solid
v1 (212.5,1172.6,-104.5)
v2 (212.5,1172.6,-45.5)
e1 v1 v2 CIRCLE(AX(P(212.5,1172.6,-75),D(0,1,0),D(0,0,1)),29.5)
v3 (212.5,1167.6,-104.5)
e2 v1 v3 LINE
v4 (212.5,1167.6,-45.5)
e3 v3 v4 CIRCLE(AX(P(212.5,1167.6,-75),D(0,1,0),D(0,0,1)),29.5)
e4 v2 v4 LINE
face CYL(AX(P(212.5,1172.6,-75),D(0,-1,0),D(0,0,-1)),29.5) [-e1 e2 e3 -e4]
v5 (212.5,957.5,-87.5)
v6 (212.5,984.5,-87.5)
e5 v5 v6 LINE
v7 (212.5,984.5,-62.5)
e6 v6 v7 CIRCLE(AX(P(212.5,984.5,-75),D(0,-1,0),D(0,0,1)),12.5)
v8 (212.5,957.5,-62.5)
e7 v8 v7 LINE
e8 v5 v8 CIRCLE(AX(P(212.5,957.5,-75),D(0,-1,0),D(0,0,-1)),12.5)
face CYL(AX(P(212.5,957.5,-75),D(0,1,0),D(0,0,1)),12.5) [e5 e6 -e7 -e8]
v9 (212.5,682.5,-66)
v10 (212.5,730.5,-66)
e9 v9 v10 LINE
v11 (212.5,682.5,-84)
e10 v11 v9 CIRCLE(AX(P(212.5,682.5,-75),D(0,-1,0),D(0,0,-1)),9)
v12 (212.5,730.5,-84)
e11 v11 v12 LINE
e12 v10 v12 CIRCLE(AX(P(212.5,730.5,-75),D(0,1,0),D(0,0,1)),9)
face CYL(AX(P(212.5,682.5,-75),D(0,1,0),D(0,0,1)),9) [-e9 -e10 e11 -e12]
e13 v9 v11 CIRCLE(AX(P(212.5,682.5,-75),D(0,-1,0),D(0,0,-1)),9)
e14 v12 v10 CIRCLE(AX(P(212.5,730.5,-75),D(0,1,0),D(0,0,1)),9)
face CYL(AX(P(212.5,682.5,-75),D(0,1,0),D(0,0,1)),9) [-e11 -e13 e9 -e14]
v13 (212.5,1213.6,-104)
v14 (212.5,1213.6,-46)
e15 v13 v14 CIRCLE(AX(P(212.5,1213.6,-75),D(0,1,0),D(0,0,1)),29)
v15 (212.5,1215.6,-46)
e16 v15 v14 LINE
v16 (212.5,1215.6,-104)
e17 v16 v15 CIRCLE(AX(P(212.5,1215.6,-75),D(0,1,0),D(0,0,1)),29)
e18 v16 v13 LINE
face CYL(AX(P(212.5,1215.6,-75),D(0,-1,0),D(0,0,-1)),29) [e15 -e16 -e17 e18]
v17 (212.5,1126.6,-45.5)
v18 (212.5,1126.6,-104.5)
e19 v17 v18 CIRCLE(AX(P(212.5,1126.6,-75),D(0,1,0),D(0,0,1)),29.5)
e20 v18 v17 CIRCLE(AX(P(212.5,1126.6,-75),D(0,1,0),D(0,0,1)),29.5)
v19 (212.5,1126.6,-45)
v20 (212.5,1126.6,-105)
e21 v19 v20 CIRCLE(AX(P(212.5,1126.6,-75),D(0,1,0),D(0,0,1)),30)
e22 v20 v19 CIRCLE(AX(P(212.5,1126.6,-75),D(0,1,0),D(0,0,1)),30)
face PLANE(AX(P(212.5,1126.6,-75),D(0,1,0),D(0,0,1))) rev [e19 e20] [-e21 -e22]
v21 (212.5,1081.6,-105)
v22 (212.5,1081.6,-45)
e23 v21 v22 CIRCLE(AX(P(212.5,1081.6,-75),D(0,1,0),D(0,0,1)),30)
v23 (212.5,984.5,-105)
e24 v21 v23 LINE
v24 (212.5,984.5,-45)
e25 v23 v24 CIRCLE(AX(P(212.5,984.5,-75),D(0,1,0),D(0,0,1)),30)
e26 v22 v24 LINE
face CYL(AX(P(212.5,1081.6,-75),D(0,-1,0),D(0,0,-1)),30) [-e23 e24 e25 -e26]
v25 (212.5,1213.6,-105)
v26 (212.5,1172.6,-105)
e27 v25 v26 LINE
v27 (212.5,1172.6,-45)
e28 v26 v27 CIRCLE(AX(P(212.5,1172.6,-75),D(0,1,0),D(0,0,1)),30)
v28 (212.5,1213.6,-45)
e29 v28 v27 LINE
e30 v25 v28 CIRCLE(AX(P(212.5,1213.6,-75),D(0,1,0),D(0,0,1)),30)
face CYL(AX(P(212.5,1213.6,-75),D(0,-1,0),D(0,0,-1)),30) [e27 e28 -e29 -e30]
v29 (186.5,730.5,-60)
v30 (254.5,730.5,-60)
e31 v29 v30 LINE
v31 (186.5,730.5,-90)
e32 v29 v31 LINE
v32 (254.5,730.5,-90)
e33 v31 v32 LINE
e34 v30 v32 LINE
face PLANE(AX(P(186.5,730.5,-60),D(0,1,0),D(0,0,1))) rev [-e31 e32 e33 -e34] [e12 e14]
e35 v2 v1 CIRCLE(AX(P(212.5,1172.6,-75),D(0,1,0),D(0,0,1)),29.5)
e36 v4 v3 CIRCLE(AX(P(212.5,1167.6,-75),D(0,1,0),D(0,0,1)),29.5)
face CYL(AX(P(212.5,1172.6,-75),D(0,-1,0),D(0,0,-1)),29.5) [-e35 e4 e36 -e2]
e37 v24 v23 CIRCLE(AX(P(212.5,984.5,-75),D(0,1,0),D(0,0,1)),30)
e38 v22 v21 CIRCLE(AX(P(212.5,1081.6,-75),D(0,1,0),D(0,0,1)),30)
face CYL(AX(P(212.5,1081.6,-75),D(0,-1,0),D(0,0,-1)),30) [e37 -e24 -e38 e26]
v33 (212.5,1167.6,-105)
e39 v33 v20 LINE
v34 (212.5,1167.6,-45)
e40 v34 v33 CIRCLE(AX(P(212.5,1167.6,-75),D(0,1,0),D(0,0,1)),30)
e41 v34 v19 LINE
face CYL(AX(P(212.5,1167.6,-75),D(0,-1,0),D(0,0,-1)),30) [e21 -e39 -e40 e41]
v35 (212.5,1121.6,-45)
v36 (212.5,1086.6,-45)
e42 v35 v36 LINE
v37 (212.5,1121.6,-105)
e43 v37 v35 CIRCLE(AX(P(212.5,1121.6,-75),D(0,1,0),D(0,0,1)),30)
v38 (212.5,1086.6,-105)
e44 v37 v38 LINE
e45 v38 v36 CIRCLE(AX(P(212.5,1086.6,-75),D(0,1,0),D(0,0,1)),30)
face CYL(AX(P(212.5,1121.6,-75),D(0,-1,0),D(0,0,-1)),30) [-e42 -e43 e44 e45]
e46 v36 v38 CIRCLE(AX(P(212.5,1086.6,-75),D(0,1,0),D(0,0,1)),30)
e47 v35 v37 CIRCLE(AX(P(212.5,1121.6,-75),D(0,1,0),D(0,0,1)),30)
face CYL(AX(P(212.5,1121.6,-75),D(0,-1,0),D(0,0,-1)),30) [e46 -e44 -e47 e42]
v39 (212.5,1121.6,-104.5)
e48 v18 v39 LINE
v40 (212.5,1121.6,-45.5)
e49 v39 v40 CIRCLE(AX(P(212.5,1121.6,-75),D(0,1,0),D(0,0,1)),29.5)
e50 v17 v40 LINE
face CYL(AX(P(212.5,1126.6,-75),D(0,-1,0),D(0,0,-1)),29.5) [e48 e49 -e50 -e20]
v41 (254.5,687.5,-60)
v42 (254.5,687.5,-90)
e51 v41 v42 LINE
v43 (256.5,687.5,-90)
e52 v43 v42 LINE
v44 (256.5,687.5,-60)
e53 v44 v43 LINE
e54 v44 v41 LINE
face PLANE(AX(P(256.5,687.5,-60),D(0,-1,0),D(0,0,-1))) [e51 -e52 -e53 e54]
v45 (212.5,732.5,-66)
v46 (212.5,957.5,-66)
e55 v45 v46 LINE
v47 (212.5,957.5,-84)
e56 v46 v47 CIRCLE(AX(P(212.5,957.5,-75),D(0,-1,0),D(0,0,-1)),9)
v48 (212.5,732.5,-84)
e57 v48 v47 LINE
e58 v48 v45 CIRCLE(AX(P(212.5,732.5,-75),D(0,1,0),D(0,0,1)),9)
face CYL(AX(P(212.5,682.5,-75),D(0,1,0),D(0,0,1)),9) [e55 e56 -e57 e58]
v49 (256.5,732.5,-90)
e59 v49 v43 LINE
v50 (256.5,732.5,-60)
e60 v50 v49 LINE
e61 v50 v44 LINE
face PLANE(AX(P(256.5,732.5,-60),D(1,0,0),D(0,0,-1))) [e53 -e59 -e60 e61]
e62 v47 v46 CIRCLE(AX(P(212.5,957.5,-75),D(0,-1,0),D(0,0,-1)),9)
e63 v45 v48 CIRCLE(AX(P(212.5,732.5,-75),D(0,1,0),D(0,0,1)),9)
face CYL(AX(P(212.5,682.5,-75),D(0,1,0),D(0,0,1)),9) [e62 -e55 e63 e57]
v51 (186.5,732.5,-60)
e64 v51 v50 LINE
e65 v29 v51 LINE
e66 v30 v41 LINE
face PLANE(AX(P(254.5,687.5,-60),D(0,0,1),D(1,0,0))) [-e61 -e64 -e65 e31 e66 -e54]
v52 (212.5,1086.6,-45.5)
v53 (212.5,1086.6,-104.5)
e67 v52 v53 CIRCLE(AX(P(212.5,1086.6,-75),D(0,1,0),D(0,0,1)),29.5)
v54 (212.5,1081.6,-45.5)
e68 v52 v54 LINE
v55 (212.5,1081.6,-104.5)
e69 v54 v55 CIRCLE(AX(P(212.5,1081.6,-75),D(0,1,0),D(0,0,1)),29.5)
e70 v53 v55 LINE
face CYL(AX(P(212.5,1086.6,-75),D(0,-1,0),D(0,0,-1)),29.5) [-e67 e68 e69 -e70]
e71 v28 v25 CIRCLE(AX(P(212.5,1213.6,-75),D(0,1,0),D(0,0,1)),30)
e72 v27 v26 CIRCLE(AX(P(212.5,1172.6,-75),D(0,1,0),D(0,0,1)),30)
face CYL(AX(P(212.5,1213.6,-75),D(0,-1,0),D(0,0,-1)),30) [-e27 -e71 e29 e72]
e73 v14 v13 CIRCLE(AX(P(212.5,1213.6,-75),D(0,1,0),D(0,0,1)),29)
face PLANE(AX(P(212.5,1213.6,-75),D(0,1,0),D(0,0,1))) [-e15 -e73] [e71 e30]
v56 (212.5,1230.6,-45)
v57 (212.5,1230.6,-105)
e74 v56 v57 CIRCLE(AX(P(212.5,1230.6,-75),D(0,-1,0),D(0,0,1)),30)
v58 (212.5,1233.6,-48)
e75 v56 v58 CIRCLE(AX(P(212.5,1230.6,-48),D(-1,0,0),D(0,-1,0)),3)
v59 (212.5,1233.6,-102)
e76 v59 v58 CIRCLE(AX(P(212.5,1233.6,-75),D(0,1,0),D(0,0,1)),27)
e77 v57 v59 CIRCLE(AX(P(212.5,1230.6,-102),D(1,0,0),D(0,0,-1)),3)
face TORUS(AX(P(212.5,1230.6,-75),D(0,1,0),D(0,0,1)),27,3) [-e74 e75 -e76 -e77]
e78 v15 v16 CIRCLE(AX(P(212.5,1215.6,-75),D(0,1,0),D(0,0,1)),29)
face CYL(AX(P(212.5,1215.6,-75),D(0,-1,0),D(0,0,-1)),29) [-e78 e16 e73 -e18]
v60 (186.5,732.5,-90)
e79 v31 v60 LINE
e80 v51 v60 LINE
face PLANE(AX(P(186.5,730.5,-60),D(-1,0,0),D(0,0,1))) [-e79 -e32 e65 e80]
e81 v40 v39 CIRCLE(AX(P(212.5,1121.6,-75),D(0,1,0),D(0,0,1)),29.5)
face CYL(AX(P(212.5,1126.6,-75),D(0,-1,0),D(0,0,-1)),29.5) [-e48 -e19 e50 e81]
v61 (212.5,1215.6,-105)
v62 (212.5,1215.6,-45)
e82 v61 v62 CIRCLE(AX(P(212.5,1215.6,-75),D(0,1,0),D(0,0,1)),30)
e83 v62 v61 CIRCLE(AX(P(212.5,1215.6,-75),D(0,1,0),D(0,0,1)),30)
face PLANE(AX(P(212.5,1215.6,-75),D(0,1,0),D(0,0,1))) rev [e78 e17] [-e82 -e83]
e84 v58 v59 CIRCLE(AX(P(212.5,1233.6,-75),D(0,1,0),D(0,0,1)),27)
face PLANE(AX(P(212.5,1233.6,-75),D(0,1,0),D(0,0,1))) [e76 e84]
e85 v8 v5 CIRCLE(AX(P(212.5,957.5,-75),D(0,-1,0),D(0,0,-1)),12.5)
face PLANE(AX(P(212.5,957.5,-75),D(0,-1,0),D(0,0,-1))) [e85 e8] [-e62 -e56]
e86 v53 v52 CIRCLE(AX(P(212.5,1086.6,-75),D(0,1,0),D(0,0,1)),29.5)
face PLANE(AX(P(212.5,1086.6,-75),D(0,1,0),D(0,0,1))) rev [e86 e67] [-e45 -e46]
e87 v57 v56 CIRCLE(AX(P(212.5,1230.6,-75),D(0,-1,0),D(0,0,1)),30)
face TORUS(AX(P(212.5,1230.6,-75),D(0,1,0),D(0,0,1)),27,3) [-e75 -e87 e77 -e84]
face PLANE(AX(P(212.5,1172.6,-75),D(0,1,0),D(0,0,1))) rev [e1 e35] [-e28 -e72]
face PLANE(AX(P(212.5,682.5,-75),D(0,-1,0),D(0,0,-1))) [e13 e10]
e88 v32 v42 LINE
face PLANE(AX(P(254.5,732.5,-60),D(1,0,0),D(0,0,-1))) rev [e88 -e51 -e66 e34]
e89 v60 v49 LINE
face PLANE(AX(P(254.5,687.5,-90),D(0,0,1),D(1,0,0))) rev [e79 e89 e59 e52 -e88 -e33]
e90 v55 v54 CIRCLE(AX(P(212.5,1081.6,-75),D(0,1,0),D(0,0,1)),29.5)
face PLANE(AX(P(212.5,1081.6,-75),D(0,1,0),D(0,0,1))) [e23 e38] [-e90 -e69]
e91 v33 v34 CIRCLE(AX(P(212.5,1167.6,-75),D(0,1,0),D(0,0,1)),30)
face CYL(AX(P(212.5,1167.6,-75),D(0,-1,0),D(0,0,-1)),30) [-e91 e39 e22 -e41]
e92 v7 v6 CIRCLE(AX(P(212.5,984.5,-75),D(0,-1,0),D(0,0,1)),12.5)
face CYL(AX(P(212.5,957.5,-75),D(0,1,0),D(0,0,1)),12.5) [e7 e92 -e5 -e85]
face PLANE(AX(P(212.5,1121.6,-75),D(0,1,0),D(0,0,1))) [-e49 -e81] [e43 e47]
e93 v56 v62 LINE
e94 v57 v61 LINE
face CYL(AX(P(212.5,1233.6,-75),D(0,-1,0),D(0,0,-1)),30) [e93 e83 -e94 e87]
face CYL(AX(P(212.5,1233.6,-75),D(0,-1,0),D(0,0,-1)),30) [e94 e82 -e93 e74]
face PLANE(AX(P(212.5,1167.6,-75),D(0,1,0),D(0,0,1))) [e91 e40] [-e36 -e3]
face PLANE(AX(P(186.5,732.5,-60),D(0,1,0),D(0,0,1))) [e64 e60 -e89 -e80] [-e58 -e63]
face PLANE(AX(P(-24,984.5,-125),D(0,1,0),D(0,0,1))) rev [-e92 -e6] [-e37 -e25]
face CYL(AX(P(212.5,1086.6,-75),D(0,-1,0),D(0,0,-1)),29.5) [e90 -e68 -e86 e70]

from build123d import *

# Parameters (mm, degrees)
SKETCH_2_R           = 24
SHELL_1_T            = -5
SKETCH_4_R           = 60
EXTRUDE_1_DEPTH      = 6
SKETCH_5_W           = 200
SKETCH_5_H           = 250
EXTRUDE_2_DEPTH      = 280
SKETCH_6_R           = 30
EXTRUDE_3_DEPTH      = 97.1
SKETCH_7_R           = 29.5
EXTRUDE_4_DEPTH      = 5
SKETCH_8_R           = 30
EXTRUDE_5_DEPTH      = 35
SKETCH_9_R           = 29.5
EXTRUDE_6_DEPTH      = 5
SKETCH_10_R          = 30
EXTRUDE_7_DEPTH      = 41
SKETCH_11_R          = 29.5
EXTRUDE_8_DEPTH      = 5
SKETCH_12_R          = 30
EXTRUDE_9_DEPTH      = 41
SKETCH_13_R          = 29
EXTRUDE_10_DEPTH     = 2
SKETCH_14_R          = 30
EXTRUDE_11_DEPTH     = 18
FILLET_1_R           = 3
SKETCH_15_OUTSIDE_W  = 599.076
SKETCH_15_OUTSIDE_H  = 512.576
SKETCH_15_OUTSIDE_R  = 22.5
CUT_EXTRUDE_1_DEPTH  = 26
SKETCH_16_W          = 1000.950512006
SKETCH_16_H          = 1372.546192884
CUT_EXTRUDE_12_DEPTH = 1285.766986682
SKETCH_17_R          = 12.5
EXTRUDE_13_DEPTH     = 27
SKETCH_24_R          = 9
EXTRUDE_1_2_DEPTH    = 275
EXTRUDE_1_3_DEPTH    = 15


with BuildPart() as part:
    # 扫描4: sweep along a path in 草图1
    with BuildLine(Plane.XY) as sweep_4_path:
        Line((0, 0), (0, 202.5))
        ThreePointArc((0, 202.5), (8.786796564, 223.713203436), (30, 232.5))
        Line((30, 232.5), (182.5, 232.5))
        ThreePointArc((182.5, 232.5), (203.713203436, 241.286796564), (212.5, 262.5))
        Line((212.5, 262.5), (212.5, 698.5))
    # 草图2 → 扫描4 (sweep)
    with BuildSketch(Plane(origin=(0, 0, 0), x_dir=(1, 0, 0), z_dir=(0, 1, 0))):
        Circle(SKETCH_2_R)
    sweep(path=sweep_4_path.line)

    # 抽壳1
    shell_1_openings = [part.faces().sort_by_distance(p)[0] for p in [
        (0, 0, 0),
    ]]
    offset(amount=SHELL_1_T, openings=shell_1_openings, kind=Kind.INTERSECTION)

    # 草图4 → Extrude 1 (add)
    with BuildSketch(Plane(origin=(0, 698.5, 0), x_dir=(-1, 0, 0), z_dir=(0, 1, 0))):
        with Locations(Location((-212.5, 0, 0), (0, 0, 90))):
            Circle(SKETCH_4_R)
    extrude(amount=EXTRUDE_1_DEPTH)

    # 草图5 → 拉伸2 (add)
    with BuildSketch(Plane(origin=(0, 704.5, 0), x_dir=(-1, 0, 0), z_dir=(0, 1, 0))):
        with Locations((-212.5, 0)):
            Rectangle(SKETCH_5_W, SKETCH_5_H)
    extrude(amount=EXTRUDE_2_DEPTH)

    # 草图6 → 拉伸3 (add)
    with BuildSketch(Plane(origin=(0, 984.5, 0), x_dir=(-1, 0, 0), z_dir=(0, 1, 0))):
        with Locations(Location((-212.5, -75, 0), (0, 0, 270))):
            Circle(SKETCH_6_R)
    extrude(amount=EXTRUDE_3_DEPTH)

    # 草图7 → 拉伸4 (add)
    with BuildSketch(Plane(origin=(0, 1081.6, 0), x_dir=(-1, 0, 0), z_dir=(0, 1, 0))):
        with Locations(Location((-212.5, -75, 0), (0, 0, 90))):
            Circle(SKETCH_7_R)
    extrude(amount=EXTRUDE_4_DEPTH)

    # 草图8 → 拉伸5 (add)
    with BuildSketch(Plane(origin=(0, 1086.6, 0), x_dir=(-1, 0, 0), z_dir=(0, 1, 0))):
        with Locations(Location((-212.5, -75, 0), (0, 0, 270))):
            Circle(SKETCH_8_R)
    extrude(amount=EXTRUDE_5_DEPTH)

    # 草图9 → 拉伸6 (add)
    with BuildSketch(Plane(origin=(0, 1121.6, 0), x_dir=(-1, 0, 0), z_dir=(0, 1, 0))):
        with Locations(Location((-212.5, -75, 0), (0, 0, 90))):
            Circle(SKETCH_9_R)
    extrude(amount=EXTRUDE_6_DEPTH)

    # 草图10 → 拉伸7 (add)
    with BuildSketch(Plane(origin=(0, 1126.6, 0), x_dir=(-1, 0, 0), z_dir=(0, 1, 0))):
        with Locations(Location((-212.5, -75, 0), (0, 0, 270))):
            Circle(SKETCH_10_R)
    extrude(amount=EXTRUDE_7_DEPTH)

    # 草图11 → 拉伸8 (add)
    with BuildSketch(Plane(origin=(0, 1167.6, 0), x_dir=(-1, 0, 0), z_dir=(0, 1, 0))):
        with Locations(Location((-212.5, -75, 0), (0, 0, 90))):
            Circle(SKETCH_11_R)
    extrude(amount=EXTRUDE_8_DEPTH)

    # 草图12 → 拉伸9 (add)
    with BuildSketch(Plane(origin=(0, 1172.6, 0), x_dir=(-1, 0, 0), z_dir=(0, 1, 0))):
        with Locations(Location((-212.5, -75, 0), (0, 0, 270))):
            Circle(SKETCH_12_R)
    extrude(amount=EXTRUDE_9_DEPTH)

    # 草图13 → 拉伸10 (add)
    with BuildSketch(Plane(origin=(0, 1213.6, 0), x_dir=(-1, 0, 0), z_dir=(0, 1, 0))):
        with Locations(Location((-212.5, -75, 0), (0, 0, 90))):
            Circle(SKETCH_13_R)
    extrude(amount=EXTRUDE_10_DEPTH)

    # 草图14 → 拉伸11 (add)
    with BuildSketch(Plane(origin=(0, 1215.6, 0), x_dir=(-1, 0, 0), z_dir=(0, 1, 0))):
        with Locations(Location((-212.5, -75, 0), (0, 0, 270))):
            Circle(SKETCH_14_R)
    extrude(amount=EXTRUDE_11_DEPTH)

    # 圆角1
    fillet_1_edges = [part.edges().sort_by_distance(p)[0] for p in [
        (212.5, 1233.6, -45),
    ]]
    fillet(fillet_1_edges, radius=FILLET_1_R)

    # 草图15 outside → 切除-拉伸1 (cut)
    with BuildSketch(Plane.XZ):
        with Locations((144.25, 0)):
            Rectangle(SKETCH_15_OUTSIDE_W, SKETCH_15_OUTSIDE_H)
        with Locations(Location((0, 0, 0), (0, 0, 270))):
            Circle(SKETCH_15_OUTSIDE_R, mode=Mode.SUBTRACT)
    extrude(amount=-CUT_EXTRUDE_1_DEPTH, mode=Mode.SUBTRACT)

    # 草图16 → 拉伸12 (cut, through all)
    with BuildSketch(Plane(origin=(312.5, 0, 0), x_dir=(0, 0, -1), z_dir=(1, 0, 0))):
        with Locations((-375.475256003, 298.226903558)):
            Rectangle(SKETCH_16_W, SKETCH_16_H)
    extrude(amount=-CUT_EXTRUDE_12_DEPTH, mode=Mode.SUBTRACT)

    # 草图17 → 拉伸13 (add)
    with BuildSketch(Plane.XZ.offset(-984.5)):
        with Locations(Location((212.5, -75, 0), (0, 0, 90))):
            Circle(SKETCH_17_R)
    extrude(amount=EXTRUDE_13_DEPTH)

    # 草图24 → Extrude 1 2 (add)
    with BuildSketch(Plane.XZ.offset(-957.5)):
        with Locations(Location((212.5, -75, 0), (0, 0, 270))):
            Circle(SKETCH_24_R)
    extrude(amount=EXTRUDE_1_2_DEPTH)

    # 草图26 → Extrude 1 3 (add, symmetric)
    with BuildSketch(Plane.XY.offset(-75)):
        Polygon((186.5, 732.5), (256.5, 732.5), (256.5, 687.5), (254.5, 687.5), (254.5, 730.5), (186.5, 730.5), align=None)
    extrude(amount=EXTRUDE_1_3_DEPTH, both=True)


solid = part.part
